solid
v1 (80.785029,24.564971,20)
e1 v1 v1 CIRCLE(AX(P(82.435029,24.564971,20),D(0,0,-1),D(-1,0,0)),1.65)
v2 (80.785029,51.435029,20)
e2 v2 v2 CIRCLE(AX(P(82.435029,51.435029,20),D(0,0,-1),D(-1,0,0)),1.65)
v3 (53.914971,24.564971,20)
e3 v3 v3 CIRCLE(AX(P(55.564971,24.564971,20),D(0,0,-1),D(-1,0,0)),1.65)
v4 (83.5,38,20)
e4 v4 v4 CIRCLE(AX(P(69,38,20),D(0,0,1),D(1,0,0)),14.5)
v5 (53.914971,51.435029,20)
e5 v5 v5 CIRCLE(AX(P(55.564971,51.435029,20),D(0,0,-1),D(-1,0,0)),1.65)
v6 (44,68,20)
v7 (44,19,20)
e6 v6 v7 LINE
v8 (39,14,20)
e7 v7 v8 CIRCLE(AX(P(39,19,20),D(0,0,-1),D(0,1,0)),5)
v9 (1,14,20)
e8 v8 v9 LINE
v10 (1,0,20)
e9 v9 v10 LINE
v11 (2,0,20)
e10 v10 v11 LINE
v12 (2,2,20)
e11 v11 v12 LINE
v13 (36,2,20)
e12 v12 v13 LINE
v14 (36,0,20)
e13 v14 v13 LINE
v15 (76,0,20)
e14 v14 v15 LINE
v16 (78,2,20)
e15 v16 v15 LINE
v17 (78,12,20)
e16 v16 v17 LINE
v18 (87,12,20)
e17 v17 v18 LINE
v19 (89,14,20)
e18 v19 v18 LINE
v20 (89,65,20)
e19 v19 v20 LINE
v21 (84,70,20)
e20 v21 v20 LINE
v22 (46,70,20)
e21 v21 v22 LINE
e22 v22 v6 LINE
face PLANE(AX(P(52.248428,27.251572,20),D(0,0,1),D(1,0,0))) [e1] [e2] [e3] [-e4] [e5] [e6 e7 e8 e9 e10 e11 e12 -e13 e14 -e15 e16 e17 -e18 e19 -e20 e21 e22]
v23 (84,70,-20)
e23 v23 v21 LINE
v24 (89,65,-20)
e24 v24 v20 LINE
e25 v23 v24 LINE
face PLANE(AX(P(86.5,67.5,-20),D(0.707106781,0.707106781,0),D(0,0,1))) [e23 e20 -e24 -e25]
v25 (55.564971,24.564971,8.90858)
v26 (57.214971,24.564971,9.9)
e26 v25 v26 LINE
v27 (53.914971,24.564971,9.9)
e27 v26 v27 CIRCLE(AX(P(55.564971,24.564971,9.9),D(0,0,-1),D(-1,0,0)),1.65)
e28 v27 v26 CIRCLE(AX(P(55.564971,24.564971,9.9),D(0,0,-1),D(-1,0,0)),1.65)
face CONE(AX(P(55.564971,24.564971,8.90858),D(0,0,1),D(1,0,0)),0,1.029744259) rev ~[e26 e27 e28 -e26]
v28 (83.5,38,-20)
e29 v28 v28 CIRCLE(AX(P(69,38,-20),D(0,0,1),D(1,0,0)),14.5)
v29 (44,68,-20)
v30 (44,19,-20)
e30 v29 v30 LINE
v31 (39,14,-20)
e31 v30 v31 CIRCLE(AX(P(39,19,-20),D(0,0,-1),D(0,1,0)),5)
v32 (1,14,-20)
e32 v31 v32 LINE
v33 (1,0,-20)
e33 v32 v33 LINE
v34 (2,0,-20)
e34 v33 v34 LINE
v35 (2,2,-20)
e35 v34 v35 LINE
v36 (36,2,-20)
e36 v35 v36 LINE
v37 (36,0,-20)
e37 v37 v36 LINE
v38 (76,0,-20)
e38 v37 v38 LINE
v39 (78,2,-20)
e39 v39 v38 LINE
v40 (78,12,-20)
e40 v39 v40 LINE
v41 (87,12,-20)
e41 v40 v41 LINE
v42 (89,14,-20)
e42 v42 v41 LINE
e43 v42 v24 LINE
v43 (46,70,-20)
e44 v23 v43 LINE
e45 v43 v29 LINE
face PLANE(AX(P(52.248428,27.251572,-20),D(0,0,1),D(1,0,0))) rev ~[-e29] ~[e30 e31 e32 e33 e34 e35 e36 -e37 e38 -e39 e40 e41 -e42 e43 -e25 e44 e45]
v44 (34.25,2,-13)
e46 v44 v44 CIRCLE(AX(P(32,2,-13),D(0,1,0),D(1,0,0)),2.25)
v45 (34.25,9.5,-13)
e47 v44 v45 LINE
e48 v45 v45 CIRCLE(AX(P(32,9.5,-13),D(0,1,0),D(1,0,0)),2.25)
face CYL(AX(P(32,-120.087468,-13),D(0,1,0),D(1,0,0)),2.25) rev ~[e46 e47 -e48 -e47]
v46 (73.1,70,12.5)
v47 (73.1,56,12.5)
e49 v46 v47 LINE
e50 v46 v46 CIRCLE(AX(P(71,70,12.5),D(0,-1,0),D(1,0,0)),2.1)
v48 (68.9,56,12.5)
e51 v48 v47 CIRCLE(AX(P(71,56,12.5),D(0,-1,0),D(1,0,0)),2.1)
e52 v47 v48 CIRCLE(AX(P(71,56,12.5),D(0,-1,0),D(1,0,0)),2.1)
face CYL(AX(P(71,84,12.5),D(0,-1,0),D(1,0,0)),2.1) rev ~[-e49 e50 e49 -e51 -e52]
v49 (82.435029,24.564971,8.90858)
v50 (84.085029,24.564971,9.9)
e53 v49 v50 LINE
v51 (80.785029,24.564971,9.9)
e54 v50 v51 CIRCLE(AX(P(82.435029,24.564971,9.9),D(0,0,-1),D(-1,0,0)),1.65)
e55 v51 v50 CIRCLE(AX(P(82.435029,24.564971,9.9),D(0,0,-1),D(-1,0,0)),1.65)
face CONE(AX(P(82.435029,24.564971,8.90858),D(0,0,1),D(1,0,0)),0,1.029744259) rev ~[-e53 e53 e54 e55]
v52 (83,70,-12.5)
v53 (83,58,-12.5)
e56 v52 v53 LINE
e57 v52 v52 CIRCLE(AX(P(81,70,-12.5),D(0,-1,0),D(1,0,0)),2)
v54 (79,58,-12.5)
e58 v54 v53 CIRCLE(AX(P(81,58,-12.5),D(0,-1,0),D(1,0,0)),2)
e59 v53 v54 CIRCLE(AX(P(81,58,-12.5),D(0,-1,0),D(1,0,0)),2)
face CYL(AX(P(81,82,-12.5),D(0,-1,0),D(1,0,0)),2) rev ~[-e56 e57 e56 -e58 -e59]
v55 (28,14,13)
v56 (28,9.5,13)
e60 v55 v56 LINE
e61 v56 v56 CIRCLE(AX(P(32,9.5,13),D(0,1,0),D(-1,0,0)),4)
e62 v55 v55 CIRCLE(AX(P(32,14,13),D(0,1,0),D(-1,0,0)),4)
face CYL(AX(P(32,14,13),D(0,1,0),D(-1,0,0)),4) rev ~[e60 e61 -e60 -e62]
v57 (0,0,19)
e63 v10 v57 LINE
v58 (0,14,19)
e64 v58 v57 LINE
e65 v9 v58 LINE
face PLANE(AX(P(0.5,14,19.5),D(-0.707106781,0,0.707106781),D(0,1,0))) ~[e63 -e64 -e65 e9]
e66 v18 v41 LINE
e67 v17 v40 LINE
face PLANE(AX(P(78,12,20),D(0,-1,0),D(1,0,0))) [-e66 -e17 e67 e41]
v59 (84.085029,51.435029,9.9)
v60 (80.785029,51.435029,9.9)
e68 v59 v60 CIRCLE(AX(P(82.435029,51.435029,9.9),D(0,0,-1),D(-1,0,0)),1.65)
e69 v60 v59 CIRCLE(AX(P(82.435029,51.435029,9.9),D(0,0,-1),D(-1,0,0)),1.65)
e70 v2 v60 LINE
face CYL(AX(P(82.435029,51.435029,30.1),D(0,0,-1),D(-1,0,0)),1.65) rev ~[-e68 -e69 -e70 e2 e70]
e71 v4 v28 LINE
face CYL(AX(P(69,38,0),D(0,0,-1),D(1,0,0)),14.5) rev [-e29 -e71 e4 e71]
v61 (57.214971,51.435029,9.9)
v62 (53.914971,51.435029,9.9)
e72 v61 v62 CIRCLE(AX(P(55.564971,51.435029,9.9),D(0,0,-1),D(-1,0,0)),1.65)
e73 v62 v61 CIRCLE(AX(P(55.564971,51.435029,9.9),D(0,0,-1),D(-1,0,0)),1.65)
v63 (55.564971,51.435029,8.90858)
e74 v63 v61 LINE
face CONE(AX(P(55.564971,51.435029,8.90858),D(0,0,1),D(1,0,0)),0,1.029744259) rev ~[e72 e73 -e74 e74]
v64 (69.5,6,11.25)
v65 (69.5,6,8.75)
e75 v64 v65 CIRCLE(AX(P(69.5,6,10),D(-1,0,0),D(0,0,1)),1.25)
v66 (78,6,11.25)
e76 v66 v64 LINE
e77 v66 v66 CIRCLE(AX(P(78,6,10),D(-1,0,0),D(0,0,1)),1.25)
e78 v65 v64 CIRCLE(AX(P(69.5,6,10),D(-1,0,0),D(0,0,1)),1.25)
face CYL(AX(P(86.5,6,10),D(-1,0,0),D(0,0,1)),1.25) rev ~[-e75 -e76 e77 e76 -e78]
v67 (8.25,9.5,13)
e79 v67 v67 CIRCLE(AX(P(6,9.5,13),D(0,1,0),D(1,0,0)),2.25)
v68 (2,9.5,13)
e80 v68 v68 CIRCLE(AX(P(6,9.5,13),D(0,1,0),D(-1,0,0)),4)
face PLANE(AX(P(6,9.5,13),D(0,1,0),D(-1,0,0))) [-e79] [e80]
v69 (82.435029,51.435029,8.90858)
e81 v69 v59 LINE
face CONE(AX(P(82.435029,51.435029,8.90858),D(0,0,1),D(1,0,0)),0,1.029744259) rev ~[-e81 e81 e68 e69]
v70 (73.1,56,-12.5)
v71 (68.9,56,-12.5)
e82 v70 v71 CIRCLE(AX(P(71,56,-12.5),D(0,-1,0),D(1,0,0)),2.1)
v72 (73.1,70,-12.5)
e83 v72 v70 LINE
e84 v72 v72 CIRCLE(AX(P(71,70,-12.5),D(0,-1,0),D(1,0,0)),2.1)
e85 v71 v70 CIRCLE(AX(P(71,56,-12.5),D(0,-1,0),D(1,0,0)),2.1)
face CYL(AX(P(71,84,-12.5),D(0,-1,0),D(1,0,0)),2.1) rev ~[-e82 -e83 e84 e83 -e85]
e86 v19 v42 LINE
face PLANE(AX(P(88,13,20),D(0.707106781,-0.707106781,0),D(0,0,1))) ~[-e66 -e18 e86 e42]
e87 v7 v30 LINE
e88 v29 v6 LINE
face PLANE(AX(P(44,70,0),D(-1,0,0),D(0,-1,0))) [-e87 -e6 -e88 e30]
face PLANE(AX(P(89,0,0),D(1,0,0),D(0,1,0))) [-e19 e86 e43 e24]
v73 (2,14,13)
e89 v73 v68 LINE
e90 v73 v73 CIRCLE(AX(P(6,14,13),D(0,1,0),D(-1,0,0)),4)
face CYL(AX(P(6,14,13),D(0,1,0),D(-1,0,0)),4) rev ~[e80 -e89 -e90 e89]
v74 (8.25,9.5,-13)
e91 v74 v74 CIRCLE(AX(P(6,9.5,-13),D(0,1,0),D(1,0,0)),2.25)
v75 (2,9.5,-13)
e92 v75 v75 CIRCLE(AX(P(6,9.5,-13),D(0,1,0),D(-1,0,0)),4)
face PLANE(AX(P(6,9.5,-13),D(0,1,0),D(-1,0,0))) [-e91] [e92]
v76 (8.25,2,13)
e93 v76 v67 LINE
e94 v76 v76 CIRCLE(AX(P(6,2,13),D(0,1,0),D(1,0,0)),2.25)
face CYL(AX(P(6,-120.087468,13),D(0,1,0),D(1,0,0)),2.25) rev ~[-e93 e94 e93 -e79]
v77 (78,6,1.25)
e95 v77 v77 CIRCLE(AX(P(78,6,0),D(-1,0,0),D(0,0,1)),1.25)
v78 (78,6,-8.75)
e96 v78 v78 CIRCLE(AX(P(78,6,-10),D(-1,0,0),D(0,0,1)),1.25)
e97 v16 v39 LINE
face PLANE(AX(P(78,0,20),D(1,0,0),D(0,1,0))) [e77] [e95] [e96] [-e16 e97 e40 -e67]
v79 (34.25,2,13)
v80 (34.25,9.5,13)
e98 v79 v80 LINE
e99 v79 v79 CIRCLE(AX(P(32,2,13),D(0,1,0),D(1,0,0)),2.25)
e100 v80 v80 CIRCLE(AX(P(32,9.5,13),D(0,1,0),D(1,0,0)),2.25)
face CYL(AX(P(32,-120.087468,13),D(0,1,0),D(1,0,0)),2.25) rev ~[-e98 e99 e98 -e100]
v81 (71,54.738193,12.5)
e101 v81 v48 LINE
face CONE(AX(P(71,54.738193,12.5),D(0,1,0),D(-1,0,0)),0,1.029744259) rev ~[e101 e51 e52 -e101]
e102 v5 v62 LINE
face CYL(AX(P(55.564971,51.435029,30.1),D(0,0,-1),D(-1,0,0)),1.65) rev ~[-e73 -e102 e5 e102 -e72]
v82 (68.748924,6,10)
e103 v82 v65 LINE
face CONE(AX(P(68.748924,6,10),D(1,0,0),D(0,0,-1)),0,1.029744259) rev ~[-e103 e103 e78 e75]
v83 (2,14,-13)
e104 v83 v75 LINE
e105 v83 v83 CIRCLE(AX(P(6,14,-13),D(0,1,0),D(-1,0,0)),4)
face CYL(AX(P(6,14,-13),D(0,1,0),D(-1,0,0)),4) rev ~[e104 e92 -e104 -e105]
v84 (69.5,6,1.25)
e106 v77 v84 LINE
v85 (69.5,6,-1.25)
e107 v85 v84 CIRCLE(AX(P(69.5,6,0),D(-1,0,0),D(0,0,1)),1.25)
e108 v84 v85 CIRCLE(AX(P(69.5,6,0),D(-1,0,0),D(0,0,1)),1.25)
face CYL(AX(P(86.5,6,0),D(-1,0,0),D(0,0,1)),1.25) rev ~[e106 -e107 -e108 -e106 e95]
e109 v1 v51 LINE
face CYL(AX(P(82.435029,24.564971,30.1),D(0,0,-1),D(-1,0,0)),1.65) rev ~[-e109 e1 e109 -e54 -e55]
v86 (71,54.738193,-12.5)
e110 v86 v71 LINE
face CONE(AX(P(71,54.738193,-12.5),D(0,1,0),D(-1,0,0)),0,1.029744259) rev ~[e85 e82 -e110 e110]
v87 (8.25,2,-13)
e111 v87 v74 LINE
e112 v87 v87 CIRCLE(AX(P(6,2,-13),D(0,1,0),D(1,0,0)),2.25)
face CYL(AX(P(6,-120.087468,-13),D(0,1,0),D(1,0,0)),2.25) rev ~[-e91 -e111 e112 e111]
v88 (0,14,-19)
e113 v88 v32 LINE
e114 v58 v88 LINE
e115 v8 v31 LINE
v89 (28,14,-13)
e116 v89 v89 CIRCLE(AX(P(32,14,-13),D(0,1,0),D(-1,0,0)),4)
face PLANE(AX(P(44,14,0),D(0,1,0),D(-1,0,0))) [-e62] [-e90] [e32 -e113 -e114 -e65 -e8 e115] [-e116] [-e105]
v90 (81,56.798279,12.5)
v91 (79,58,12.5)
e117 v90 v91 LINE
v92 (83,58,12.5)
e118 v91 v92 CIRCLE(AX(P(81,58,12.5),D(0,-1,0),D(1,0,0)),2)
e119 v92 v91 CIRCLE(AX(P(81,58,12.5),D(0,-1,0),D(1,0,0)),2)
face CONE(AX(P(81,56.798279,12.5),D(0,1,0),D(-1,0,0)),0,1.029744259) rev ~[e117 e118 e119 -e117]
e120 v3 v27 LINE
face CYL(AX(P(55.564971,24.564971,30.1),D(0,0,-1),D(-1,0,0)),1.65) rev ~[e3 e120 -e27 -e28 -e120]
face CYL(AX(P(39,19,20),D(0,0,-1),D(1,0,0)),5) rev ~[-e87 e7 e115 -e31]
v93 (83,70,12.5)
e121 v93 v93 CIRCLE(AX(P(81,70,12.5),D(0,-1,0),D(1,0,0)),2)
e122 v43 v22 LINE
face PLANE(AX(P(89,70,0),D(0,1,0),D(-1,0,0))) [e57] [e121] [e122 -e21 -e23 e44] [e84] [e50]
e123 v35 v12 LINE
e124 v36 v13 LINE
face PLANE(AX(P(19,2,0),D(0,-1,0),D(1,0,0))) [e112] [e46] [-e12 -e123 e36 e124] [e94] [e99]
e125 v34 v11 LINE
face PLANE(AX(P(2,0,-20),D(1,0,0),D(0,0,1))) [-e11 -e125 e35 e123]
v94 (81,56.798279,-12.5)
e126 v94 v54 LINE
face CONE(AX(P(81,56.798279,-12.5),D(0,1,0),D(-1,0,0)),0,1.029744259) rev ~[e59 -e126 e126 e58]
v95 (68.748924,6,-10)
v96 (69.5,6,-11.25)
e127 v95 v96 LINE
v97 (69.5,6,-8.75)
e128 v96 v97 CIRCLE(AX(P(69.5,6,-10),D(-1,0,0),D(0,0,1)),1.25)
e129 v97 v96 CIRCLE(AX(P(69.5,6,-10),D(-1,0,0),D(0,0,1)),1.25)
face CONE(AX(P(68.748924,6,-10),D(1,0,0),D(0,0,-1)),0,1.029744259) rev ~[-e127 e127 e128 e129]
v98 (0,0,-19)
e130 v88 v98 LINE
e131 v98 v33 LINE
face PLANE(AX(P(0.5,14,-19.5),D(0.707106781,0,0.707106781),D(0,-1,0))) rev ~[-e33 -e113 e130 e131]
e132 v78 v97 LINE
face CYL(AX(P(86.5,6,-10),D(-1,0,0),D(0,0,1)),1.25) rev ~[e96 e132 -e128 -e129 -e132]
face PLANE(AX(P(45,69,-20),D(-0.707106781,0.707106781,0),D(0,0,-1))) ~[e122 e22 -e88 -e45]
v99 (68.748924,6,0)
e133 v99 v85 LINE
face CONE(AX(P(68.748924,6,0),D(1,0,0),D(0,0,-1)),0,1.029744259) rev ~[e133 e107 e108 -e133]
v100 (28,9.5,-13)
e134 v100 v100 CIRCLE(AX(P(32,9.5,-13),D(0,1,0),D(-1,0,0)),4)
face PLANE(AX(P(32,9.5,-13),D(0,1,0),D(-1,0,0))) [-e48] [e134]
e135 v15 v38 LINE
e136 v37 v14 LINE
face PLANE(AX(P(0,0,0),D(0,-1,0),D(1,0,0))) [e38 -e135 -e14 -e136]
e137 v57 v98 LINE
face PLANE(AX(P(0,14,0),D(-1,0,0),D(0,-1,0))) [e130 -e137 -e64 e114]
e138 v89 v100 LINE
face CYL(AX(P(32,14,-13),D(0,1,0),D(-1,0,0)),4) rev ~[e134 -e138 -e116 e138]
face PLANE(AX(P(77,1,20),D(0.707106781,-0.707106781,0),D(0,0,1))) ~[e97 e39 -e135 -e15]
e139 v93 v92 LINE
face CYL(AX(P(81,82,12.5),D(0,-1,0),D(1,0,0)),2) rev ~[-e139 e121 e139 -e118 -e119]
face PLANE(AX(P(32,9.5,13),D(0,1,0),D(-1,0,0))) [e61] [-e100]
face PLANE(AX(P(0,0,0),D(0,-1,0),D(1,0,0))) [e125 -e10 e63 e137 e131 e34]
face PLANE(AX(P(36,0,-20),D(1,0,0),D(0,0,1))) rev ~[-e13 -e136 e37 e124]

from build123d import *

# Parameters (mm, degrees)
SKETCH1_R                    = 14.5
BOSS_EXTRUDE1_DEPTH          = 20
F_4_5_4_5_DIAMETER_HOLE1_D   = 4.5
SKETCH5_W                    = 34
SKETCH5_H                    = 40
CUT_EXTRUDE1_DEPTH           = 2
M4_TAPPED_HOLE1_D            = 3.3
M4_TAPPED_HOLE1_DEPTH        = 10.1
M4_TAPPED_HOLE1_TIP          = 0.991420021
M5_TAPPED_HOLE1_D            = 4.2
M5_TAPPED_HOLE1_DEPTH        = 14
M5_TAPPED_HOLE1_TIP          = 1.2618073
F_4_0_4_DIAMETER_HOLE1_D     = 4
F_4_0_4_DIAMETER_HOLE1_DEPTH = 12
F_4_0_4_DIAMETER_HOLE1_TIP   = 1.201721238
SKETCH12_W                   = 11
SKETCH12_H                   = 12
CUT_EXTRUDE2_DEPTH           = 121.087468122
M3_TAPPED_HOLE1_D            = 2.5
M3_TAPPED_HOLE1_DEPTH        = 8.5
M3_TAPPED_HOLE1_TIP          = 0.751075774
CHAMFER1_SIZE                = 5
CHAMFER2_SIZE                = 2
SKETCH15_R                   = 4
CUT_EXTRUDE3_DEPTH           = 4.5
FILLET1_R                    = 5
CHAMFER3_SIZE                = 1


with BuildPart() as part:
    # Sketch1 → Boss-Extrude1 (new, symmetric)
    with BuildSketch(Plane.XY):
        Polygon((0, 0), (89, 0), (89, 70), (44, 70), (44, 14), (0, 14), align=None)
        with Locations((69, 38)):
            Circle(SKETCH1_R, mode=Mode.SUBTRACT)
    extrude(amount=BOSS_EXTRUDE1_DEPTH, both=True)

    # Ø4.5 (4.5) Diameter Hole1 (through all)
    with Locations(Plane(origin=(0, 0, 0), x_dir=(-1, 0, 0), z_dir=(0, -1, 0))):
        with Locations((-32, 13), (-6, 13), (-6, -13), (-32, -13)):
            Hole(F_4_5_4_5_DIAMETER_HOLE1_D / 2)

    # Sketch5 → Cut-Extrude1 (cut)
    with BuildSketch(Plane.XZ):
        with Locations((19, 0)):
            Rectangle(SKETCH5_W, SKETCH5_H)
    extrude(amount=-CUT_EXTRUDE1_DEPTH, mode=Mode.SUBTRACT)

    # M4 Tapped Hole1
    with Locations(Plane.XY.offset(20)):
        with Locations((55.564971157, 51.435028843), (82.435028843, 51.435028843), (55.564971157, 24.564971157), (82.435028843, 24.564971157)):
            Hole(M4_TAPPED_HOLE1_D / 2, depth=M4_TAPPED_HOLE1_DEPTH)
            with Locations((0, 0, -(M4_TAPPED_HOLE1_DEPTH + M4_TAPPED_HOLE1_TIP / 2))):  # 118° drill point
                Cone(0, M4_TAPPED_HOLE1_D / 2, M4_TAPPED_HOLE1_TIP, mode=Mode.SUBTRACT)

    # M5 Tapped Hole1
    with Locations(Plane(origin=(0, 70, 0), x_dir=(-1, 0, 0), z_dir=(0, 1, 0))):
        with Locations((-71, -12.5), (-71, 12.5)):
            Hole(M5_TAPPED_HOLE1_D / 2, depth=M5_TAPPED_HOLE1_DEPTH)
            with Locations((0, 0, -(M5_TAPPED_HOLE1_DEPTH + M5_TAPPED_HOLE1_TIP / 2))):  # 118° drill point
                Cone(0, M5_TAPPED_HOLE1_D / 2, M5_TAPPED_HOLE1_TIP, mode=Mode.SUBTRACT)

    # Ø4.0 (4) Diameter Hole1
    with Locations(Plane(origin=(0, 70, 0), x_dir=(-1, 0, 0), z_dir=(0, 1, 0))):
        with Locations((-81, 12.5), (-81, -12.5)):
            Hole(F_4_0_4_DIAMETER_HOLE1_D / 2, depth=F_4_0_4_DIAMETER_HOLE1_DEPTH)
            with Locations((0, 0, -(F_4_0_4_DIAMETER_HOLE1_DEPTH + F_4_0_4_DIAMETER_HOLE1_TIP / 2))):  # 118° drill point
                Cone(0, F_4_0_4_DIAMETER_HOLE1_D / 2, F_4_0_4_DIAMETER_HOLE1_TIP, mode=Mode.SUBTRACT)

    # Sketch12 → Cut-Extrude2 (cut, through all)
    with BuildSketch(Plane.XY.offset(20)):
        with Locations((83.5, 6)):
            Rectangle(SKETCH12_W, SKETCH12_H)
    extrude(amount=-CUT_EXTRUDE2_DEPTH, mode=Mode.SUBTRACT)

    # M3 Tapped Hole1
    with Locations(Plane(origin=(78, 0, 0), x_dir=(0, 0, -1), z_dir=(1, 0, 0))):
        with Locations((-10, 6), (0, 6), (10, 6)):
            Hole(M3_TAPPED_HOLE1_D / 2, depth=M3_TAPPED_HOLE1_DEPTH)
            with Locations((0, 0, -(M3_TAPPED_HOLE1_DEPTH + M3_TAPPED_HOLE1_TIP / 2))):  # 118° drill point
                Cone(0, M3_TAPPED_HOLE1_D / 2, M3_TAPPED_HOLE1_TIP, mode=Mode.SUBTRACT)

    # Chamfer1
    chamfer1_edges = [part.edges().sort_by_distance(p)[0] for p in [
        (89, 70, 0),
    ]]
    chamfer(chamfer1_edges, length=CHAMFER1_SIZE)

    # Chamfer2
    chamfer2_edges = [part.edges().sort_by_distance(p)[0] for p in [
        (44, 70, 0),
        (89, 12, 0),
        (78, 0, 0),
    ]]
    chamfer(chamfer2_edges, length=CHAMFER2_SIZE)

    # Sketch15 → Cut-Extrude3 (cut)
    with BuildSketch(Plane(origin=(0, 14, 0), x_dir=(1, 0, 0), z_dir=(0, 1, 0))):
        with Locations(Location((6, 13, 0), (0, 0, 180))):
            Circle(SKETCH15_R)
        with Locations(Location((32, 13, 0), (0, 0, 180))):
            Circle(SKETCH15_R)
        with Locations(Location((32, -13, 0), (0, 0, 180))):
            Circle(SKETCH15_R)
        with Locations(Location((6, -13, 0), (0, 0, 180))):
            Circle(SKETCH15_R)
    extrude(amount=-CUT_EXTRUDE3_DEPTH, mode=Mode.SUBTRACT)

    # Fillet1
    fillet1_edges = [part.edges().sort_by_distance(p)[0] for p in [
        (44, 14, 0),
    ]]
    fillet(fillet1_edges, radius=FILLET1_R)

    # Chamfer3
    chamfer3_edges = [part.edges().sort_by_distance(p)[0] for p in [
        (0, 7, 20),
        (0, 7, -20),
    ]]
    chamfer(chamfer3_edges, length=CHAMFER3_SIZE)


solid = part.part
